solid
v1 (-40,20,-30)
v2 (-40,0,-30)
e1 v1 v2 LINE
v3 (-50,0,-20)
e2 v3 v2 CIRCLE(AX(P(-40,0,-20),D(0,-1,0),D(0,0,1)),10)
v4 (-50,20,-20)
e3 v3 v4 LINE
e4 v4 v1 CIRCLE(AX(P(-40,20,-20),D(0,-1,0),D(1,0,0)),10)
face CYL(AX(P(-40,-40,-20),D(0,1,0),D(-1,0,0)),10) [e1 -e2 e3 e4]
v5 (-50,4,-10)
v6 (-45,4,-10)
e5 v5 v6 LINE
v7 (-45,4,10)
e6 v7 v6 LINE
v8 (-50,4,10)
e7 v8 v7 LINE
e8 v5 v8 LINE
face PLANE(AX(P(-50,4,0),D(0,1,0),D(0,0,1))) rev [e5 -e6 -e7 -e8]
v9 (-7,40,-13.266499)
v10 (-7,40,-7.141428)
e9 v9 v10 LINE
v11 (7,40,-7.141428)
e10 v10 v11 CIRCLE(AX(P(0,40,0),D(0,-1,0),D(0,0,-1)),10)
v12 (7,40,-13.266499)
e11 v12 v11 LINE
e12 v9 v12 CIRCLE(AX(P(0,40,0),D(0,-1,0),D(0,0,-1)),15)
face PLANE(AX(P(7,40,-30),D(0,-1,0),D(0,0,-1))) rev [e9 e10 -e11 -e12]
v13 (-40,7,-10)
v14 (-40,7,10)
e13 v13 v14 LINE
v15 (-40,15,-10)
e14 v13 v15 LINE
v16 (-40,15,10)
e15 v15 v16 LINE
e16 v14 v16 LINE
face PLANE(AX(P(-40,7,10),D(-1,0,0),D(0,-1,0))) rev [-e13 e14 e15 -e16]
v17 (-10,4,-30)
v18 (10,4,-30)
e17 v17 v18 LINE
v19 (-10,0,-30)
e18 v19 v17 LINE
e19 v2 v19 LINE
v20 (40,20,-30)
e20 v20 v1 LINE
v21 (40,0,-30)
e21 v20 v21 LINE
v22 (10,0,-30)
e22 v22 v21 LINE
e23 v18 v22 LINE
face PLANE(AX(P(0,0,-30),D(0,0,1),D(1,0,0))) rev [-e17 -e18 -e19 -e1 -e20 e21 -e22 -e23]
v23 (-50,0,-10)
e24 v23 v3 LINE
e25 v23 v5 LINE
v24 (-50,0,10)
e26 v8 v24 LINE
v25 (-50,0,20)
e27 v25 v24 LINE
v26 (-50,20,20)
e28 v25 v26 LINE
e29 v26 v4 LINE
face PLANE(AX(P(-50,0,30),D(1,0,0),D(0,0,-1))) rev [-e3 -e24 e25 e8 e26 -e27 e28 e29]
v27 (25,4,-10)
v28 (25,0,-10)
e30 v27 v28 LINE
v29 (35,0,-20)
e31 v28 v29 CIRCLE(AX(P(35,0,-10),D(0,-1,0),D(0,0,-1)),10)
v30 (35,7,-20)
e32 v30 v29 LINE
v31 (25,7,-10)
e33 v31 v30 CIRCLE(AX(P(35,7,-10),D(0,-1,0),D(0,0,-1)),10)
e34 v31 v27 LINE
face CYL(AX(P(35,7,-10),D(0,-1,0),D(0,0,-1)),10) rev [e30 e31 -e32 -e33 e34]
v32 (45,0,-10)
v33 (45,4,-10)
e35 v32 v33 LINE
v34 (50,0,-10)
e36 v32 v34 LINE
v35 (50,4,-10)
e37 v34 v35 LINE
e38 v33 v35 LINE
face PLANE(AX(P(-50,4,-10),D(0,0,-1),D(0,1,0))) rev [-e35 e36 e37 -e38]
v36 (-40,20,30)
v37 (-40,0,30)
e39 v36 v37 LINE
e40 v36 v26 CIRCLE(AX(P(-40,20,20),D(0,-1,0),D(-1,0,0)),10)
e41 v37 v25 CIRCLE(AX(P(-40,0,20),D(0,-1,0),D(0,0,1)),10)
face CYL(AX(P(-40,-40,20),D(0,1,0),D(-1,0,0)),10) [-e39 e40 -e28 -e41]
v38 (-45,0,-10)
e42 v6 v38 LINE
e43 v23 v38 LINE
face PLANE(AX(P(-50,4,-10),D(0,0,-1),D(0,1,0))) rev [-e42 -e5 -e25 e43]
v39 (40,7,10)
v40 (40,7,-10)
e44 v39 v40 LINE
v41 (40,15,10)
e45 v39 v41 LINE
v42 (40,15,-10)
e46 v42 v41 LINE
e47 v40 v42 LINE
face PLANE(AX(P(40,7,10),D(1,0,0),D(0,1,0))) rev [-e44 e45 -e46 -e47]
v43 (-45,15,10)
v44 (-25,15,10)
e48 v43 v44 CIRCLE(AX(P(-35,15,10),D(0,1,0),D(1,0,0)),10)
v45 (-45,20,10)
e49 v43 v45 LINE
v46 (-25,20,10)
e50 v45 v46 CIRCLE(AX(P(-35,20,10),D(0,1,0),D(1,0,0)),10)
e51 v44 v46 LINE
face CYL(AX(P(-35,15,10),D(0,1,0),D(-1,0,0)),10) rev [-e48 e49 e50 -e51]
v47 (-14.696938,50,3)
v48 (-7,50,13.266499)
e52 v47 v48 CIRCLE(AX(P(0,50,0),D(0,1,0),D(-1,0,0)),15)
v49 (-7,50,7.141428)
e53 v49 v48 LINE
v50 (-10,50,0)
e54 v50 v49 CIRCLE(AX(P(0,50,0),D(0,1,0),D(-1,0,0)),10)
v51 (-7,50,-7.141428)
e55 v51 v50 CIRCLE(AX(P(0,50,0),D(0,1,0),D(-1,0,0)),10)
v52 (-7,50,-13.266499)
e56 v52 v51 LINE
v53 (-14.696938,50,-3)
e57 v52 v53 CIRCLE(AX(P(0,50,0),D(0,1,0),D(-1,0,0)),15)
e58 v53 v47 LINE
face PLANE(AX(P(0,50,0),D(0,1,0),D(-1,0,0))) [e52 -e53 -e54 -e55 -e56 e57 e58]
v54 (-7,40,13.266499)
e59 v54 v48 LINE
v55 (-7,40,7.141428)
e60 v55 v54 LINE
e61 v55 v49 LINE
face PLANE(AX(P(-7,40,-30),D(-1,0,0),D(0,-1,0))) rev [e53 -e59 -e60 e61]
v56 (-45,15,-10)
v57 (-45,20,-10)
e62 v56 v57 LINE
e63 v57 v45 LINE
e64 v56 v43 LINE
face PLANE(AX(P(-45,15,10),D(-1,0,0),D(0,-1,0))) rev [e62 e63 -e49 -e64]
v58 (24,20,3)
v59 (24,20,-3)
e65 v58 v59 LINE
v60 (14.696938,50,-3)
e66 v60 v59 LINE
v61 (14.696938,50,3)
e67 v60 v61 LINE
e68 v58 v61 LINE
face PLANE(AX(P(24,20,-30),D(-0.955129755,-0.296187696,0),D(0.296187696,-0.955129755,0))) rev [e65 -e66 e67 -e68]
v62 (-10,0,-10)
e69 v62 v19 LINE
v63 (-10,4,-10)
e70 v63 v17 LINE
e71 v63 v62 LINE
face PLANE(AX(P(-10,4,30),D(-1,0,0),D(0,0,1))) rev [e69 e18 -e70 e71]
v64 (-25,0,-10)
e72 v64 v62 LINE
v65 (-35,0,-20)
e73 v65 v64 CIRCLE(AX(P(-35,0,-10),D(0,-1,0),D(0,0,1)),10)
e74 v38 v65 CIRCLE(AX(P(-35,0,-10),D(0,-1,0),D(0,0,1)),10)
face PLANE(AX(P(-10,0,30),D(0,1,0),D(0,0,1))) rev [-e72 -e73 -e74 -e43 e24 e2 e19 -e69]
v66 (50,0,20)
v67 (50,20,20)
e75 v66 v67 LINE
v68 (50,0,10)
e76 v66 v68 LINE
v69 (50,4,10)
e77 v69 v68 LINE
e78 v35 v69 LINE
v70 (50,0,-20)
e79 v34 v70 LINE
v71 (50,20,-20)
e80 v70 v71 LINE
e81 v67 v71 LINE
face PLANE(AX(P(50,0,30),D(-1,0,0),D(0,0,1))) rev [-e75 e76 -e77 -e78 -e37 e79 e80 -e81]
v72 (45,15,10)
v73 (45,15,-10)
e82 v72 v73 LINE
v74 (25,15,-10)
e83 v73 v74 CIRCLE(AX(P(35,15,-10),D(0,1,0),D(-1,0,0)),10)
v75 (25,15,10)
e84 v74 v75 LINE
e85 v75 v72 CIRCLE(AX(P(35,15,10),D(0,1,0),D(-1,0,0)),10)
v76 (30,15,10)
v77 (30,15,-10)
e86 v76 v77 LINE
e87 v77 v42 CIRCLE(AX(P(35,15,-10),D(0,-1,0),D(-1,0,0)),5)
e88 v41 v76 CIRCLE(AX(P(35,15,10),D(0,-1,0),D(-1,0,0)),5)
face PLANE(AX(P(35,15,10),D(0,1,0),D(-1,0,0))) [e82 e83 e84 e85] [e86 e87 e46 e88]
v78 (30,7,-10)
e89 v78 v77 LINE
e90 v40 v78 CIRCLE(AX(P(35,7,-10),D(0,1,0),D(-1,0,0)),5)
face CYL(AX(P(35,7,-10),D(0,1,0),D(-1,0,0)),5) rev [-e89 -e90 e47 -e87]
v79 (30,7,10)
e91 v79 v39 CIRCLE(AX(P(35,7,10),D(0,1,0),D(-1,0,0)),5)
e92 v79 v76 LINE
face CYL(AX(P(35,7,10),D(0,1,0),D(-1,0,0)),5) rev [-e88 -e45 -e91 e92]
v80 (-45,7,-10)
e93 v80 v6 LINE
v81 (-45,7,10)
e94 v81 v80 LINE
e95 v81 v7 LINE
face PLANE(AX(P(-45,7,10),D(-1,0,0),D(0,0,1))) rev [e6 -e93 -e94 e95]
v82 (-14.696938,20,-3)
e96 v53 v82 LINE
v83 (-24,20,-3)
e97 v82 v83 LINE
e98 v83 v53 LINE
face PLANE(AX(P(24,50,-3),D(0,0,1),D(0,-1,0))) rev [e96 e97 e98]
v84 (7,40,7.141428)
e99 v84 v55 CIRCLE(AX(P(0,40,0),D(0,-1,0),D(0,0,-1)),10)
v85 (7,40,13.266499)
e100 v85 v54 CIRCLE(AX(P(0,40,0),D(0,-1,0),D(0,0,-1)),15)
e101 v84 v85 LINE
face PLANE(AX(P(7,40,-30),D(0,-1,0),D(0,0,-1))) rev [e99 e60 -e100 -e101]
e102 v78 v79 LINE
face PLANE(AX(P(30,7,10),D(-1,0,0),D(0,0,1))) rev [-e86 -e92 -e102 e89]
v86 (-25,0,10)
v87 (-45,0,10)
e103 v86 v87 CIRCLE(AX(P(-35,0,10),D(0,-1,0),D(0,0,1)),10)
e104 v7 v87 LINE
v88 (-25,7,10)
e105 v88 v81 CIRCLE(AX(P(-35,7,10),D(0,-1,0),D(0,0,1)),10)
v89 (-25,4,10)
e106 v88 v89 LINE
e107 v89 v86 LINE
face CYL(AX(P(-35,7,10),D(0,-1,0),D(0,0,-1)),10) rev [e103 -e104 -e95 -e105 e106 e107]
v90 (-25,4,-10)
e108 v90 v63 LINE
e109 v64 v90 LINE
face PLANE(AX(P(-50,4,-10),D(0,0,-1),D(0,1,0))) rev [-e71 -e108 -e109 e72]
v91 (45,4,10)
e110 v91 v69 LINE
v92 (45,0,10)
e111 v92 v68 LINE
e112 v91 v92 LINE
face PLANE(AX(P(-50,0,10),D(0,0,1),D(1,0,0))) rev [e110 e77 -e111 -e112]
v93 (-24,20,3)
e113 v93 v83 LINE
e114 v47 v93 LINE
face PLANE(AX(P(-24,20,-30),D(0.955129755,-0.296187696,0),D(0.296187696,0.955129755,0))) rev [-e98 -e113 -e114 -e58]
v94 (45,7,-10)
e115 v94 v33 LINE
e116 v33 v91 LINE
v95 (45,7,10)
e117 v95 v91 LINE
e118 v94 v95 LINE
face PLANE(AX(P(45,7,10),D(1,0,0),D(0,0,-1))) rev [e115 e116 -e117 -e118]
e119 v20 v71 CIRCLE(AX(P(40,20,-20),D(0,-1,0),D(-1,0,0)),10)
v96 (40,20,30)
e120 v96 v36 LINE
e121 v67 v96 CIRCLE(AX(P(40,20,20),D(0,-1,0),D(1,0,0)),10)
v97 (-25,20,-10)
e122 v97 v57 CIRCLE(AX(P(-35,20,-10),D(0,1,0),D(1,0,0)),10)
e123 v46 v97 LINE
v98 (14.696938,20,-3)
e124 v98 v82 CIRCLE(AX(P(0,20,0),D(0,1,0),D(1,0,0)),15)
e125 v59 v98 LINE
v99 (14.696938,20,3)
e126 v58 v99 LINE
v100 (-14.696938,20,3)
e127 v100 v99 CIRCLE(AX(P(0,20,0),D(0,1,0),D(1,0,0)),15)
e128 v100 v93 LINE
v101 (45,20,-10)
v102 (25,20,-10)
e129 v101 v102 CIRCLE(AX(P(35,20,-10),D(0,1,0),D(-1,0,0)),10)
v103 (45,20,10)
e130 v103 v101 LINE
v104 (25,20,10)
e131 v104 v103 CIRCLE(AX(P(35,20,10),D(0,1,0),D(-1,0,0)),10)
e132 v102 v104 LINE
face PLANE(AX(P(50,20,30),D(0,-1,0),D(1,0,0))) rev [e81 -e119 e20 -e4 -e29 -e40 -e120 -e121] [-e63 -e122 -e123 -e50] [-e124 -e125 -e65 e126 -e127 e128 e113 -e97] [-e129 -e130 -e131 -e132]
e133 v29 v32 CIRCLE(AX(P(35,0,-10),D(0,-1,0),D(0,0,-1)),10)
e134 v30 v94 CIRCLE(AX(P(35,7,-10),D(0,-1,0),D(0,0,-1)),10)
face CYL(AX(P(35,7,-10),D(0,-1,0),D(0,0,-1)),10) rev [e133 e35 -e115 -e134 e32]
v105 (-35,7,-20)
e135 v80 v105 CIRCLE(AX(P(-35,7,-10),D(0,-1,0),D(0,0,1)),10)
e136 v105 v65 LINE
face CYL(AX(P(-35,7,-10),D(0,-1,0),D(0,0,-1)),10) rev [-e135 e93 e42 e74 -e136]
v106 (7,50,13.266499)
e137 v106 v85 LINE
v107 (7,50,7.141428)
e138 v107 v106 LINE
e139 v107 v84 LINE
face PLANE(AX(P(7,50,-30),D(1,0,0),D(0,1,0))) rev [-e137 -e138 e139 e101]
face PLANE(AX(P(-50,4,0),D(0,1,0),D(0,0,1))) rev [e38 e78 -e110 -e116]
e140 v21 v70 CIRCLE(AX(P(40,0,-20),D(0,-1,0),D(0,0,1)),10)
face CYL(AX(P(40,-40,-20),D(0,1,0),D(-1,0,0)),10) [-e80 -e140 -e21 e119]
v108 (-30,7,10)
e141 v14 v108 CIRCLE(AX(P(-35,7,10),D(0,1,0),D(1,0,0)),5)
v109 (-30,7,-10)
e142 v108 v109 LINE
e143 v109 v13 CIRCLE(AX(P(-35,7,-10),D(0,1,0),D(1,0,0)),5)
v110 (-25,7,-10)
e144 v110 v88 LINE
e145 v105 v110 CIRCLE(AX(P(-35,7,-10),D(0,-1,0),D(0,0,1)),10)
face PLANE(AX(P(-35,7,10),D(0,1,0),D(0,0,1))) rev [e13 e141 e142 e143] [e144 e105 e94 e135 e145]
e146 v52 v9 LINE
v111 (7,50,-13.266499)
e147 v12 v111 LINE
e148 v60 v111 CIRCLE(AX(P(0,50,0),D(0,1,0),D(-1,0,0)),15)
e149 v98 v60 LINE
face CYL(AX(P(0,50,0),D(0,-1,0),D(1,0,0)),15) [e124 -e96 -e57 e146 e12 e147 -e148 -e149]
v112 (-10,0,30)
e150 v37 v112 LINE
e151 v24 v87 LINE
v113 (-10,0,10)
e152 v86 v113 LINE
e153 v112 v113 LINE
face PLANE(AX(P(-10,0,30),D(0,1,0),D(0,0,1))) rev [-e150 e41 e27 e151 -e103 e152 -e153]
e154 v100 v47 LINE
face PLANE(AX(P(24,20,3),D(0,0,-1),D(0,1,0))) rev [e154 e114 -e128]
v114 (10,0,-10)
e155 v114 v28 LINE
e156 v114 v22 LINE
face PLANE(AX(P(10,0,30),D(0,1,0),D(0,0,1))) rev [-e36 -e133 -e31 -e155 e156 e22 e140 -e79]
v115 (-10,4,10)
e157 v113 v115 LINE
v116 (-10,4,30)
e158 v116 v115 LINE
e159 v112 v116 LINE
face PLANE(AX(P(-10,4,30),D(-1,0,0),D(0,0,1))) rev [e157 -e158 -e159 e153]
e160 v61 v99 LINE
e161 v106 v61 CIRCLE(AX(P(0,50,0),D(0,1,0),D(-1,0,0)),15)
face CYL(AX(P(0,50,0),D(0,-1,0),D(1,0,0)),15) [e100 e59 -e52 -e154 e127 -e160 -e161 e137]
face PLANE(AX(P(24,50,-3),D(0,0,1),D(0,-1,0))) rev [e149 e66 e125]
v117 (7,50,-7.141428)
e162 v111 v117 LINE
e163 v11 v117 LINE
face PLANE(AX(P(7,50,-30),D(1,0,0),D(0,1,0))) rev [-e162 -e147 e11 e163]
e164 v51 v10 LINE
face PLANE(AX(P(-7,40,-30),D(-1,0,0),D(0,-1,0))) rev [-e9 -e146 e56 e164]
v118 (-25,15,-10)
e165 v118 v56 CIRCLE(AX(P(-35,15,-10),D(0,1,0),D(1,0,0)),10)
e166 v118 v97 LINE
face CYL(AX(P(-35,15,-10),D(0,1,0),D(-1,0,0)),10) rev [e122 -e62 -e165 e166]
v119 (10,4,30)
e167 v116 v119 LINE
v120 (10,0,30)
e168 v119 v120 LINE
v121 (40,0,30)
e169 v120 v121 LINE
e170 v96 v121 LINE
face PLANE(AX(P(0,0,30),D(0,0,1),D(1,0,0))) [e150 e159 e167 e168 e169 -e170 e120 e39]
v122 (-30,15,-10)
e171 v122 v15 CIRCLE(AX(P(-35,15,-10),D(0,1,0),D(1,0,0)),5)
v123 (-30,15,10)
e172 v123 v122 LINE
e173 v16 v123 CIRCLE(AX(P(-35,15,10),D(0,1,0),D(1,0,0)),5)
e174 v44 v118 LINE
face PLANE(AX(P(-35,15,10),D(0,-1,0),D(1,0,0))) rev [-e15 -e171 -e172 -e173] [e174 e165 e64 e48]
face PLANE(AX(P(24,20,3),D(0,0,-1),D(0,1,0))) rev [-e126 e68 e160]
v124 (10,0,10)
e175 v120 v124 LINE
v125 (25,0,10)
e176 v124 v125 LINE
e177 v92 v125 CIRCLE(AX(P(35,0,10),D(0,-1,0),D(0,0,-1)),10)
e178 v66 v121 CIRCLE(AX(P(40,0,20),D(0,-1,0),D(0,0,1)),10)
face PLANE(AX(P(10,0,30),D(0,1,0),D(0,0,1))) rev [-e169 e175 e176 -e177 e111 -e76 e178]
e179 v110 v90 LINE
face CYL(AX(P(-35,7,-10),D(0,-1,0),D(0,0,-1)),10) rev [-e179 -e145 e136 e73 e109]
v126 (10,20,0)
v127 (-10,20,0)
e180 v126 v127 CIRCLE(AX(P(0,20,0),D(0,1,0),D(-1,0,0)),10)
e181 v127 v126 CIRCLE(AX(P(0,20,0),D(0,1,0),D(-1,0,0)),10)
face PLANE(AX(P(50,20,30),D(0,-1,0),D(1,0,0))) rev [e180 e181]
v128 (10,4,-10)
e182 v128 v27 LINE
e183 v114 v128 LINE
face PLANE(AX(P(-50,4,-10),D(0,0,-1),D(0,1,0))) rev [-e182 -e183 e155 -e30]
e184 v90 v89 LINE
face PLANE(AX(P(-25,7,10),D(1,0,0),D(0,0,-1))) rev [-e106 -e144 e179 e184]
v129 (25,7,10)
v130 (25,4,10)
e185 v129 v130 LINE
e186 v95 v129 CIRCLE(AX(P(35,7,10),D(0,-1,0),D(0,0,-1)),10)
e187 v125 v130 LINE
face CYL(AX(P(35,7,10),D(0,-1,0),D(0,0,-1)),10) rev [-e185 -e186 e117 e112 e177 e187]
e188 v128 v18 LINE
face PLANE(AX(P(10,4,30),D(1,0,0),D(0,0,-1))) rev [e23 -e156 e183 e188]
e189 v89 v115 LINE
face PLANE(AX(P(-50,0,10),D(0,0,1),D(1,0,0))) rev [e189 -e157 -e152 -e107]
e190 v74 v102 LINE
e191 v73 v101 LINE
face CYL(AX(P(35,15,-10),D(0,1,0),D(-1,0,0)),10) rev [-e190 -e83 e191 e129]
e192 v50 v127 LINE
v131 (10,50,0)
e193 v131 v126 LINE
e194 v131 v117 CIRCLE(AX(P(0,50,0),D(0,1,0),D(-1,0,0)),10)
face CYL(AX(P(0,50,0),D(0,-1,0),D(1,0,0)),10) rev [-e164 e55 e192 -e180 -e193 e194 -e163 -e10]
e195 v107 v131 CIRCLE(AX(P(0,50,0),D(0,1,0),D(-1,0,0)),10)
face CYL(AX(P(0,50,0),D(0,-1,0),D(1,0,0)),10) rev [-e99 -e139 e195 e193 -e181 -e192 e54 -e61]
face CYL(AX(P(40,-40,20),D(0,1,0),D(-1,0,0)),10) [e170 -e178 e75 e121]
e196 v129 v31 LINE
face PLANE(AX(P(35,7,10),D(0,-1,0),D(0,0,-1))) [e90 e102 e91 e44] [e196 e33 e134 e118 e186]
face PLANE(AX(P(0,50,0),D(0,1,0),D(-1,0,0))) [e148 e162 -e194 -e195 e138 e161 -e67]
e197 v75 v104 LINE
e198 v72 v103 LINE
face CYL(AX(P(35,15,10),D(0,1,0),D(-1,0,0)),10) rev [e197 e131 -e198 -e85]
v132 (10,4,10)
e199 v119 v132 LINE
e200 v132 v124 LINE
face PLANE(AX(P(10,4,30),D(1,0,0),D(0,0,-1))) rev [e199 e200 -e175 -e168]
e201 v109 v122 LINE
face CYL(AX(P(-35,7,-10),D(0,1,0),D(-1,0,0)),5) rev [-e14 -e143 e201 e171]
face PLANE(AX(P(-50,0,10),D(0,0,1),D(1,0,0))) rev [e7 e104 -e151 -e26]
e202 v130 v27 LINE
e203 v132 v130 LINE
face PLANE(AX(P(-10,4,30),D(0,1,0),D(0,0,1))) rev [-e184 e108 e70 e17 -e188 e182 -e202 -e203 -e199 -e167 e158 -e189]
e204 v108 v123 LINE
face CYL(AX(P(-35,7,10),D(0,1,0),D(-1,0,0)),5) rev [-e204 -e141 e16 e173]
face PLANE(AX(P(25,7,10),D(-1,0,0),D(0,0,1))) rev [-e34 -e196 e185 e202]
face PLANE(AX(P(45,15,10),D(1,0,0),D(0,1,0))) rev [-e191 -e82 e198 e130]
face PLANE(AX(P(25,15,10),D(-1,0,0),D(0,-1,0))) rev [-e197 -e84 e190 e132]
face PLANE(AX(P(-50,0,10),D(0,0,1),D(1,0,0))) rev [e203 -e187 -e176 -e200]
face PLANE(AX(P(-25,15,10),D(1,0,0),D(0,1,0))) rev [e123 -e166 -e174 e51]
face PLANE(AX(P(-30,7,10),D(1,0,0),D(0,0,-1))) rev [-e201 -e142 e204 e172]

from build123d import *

# Parameters (mm, degrees)
BASE_PLATE_DEPTH         = 30
UNDERSIDE_NOTCHES_DEPTH  = 60
PIVOT_BOSS_SKETCH_R      = 15
PIVOT_BOSS_SKETCH_R_2    = 10
PIVOT_BOSS_30_DEPTH      = 30
SLOT_RECESS_A_DEPTH      = 13
SLOT_INNER_CUT_A_DEPTH   = 5
SLOT_START               = -7
SLOT_RECESS_B_DEPTH      = 7
SLOT_INNER_CUT_B_DEPTH   = 116.758369028
BOSS_SLOT_CUT_DEPTH      = 77.811457479
BOSS_SLOT_CUT_DEPTH_BACK = 77.811457479
SUPPORT_RIB_DEPTH        = 24
RIB_TRIM_CUT_DEPTH       = 77.811457479
RIB_TRIM_CUT_DEPTH_BACK  = 77.811457479
PIVOT_BORE_SKETCH_R      = 10
PIVOT_BORE_20_DEPTH      = 48


with BuildPart() as part:
    # Base Plate Profile Sketch → Base Plate (new, symmetric)
    with BuildSketch(Plane.XY):
        Polygon((-10, 4), (10, 4), (10, 0), (50, 0), (50, 20), (-50, 20), (-50, 0), (-10, 0), align=None)
    extrude(amount=BASE_PLATE_DEPTH, both=True)

    # Underside Notches Sketch → Underside Notches (cut)
    with BuildSketch(Plane(origin=(0, 20, 0), x_dir=(1, 0, 0), z_dir=(0, 1, 0))):
        with BuildLine():
            Line((40, 30), (50, 30))
            Line((50, 30), (50, 20))
            ThreePointArc((50, 20), (47.071067812, 27.071067812), (40, 30))
        make_face()
        with BuildLine():
            Line((-50, 30), (-50, 20))
            ThreePointArc((-50, 20), (-47.071067812, 27.071067812), (-40, 30))
            Line((-40, 30), (-50, 30))
        make_face()
        with BuildLine():
            Line((-50, -30), (-50, -20))
            ThreePointArc((-50, -20), (-47.071067812, -27.071067812), (-40, -30))
            Line((-40, -30), (-50, -30))
        make_face()
        with BuildLine():
            Line((50, -30), (50, -20))
            ThreePointArc((50, -20), (47.071067812, -27.071067812), (40, -30))
            Line((40, -30), (50, -30))
        make_face()
    extrude(amount=-UNDERSIDE_NOTCHES_DEPTH, mode=Mode.SUBTRACT)

    # Pivot Boss Sketch → Pivot Boss Ø30 (add)
    with BuildSketch(Plane(origin=(0, 20, 0), x_dir=(1, 0, 0), z_dir=(0, 1, 0))):
        Circle(PIVOT_BOSS_SKETCH_R)
        with Locations(Location((0, 0, 0), (0, 0, 180))):
            Circle(PIVOT_BOSS_SKETCH_R_2, mode=Mode.SUBTRACT)
    extrude(amount=PIVOT_BOSS_30_DEPTH)

    # Slot Recess A Sketch → Slot Recess A (cut)
    with BuildSketch(Plane(origin=(0, 20, 0), x_dir=(1, 0, 0), z_dir=(0, 1, 0))):
        with BuildLine():
            Line((30, -10), (30, 10))
            ThreePointArc((30, 10), (35, 15), (40, 10))
            Line((40, 10), (40, -10))
            ThreePointArc((40, -10), (35, -15), (30, -10))
        make_face()
        with BuildLine():
            Line((-30, -10), (-30, 10))
            ThreePointArc((-30, 10), (-35, 15), (-40, 10))
            Line((-40, 10), (-40, -10))
            ThreePointArc((-40, -10), (-35, -15), (-30, -10))
        make_face()
    extrude(amount=-SLOT_RECESS_A_DEPTH, mode=Mode.SUBTRACT)

    # Slot Inner Cut A Sketch → Slot Inner Cut A (cut)
    with BuildSketch(Plane(origin=(0, 20, 0), x_dir=(1, 0, 0), z_dir=(0, 1, 0))):
        with BuildLine():
            Line((25, -10), (25, 10))
            ThreePointArc((25, 10), (35, 20), (45, 10))
            Line((45, 10), (45, -10))
            ThreePointArc((45, -10), (35, -20), (25, -10))
        make_face()
        with BuildLine():
            Line((-25, -10), (-25, 10))
            ThreePointArc((-25, 10), (-35, 20), (-45, 10))
            Line((-45, 10), (-45, -10))
            ThreePointArc((-45, -10), (-35, -20), (-25, -10))
        make_face()
    extrude(amount=-SLOT_INNER_CUT_A_DEPTH, mode=Mode.SUBTRACT)

    # Slot Recess B Sketch → Slot Recess B (cut)
    with BuildSketch(Plane.XZ.offset(SLOT_START)):
        with BuildLine():
            Line((45, 10), (45, -10))
            ThreePointArc((45, -10), (35, -20), (25, -10))
            Line((25, -10), (25, 10))
            ThreePointArc((25, 10), (35, 20), (45, 10))
        make_face()
        with BuildLine():
            Line((-45, 10), (-45, -10))
            ThreePointArc((-45, -10), (-35, -20), (-25, -10))
            Line((-25, -10), (-25, 10))
            ThreePointArc((-25, 10), (-35, 20), (-45, 10))
        make_face()
    extrude(amount=SLOT_RECESS_B_DEPTH, mode=Mode.SUBTRACT)

    # Slot Inner Cut B Sketch → Slot Inner Cut B (cut, through all)
    with BuildSketch(Plane(origin=(50, 0, 0), x_dir=(0, 0, -1), z_dir=(1, 0, 0))):
        Polygon((0, 4), (10, 4), (10, 0), (-10, 0), (-10, 4), align=None)
    extrude(amount=-SLOT_INNER_CUT_B_DEPTH, mode=Mode.SUBTRACT)

    # Boss Slot Sketch → Boss Slot Cut (cut, two sides: drawn at the far end of the back side and taken through both)
    with BuildSketch(Plane.XY.offset(-BOSS_SLOT_CUT_DEPTH_BACK)):
        Polygon((0, 50), (7, 50), (7, 40), (-7, 40), (-7, 50), align=None)
    extrude(amount=BOSS_SLOT_CUT_DEPTH + BOSS_SLOT_CUT_DEPTH_BACK, mode=Mode.SUBTRACT)

    # Support Rib Sketch → Support Rib (add, symmetric)
    with BuildSketch(Plane(origin=(0, 0, 0), x_dir=(0, 0, -1), z_dir=(1, 0, 0))):
        Polygon((0, 50), (3, 50), (3, 20), (-3, 20), (-3, 50), align=None)
    extrude(amount=SUPPORT_RIB_DEPTH, both=True)

    # Rib Trim Sketch → Rib Trim Cut (cut, two sides: drawn at the far end of the back side and taken through both)
    with BuildSketch(Plane.XY.offset(-RIB_TRIM_CUT_DEPTH_BACK)):
        Polygon((24, 20), (14.696938457, 50), (24, 50), align=None)
        Polygon((-24, 50), (-24, 20), (-14.696938457, 50), align=None)
    extrude(amount=RIB_TRIM_CUT_DEPTH + RIB_TRIM_CUT_DEPTH_BACK, mode=Mode.SUBTRACT)

    # Pivot Bore Sketch → Pivot Bore Ø20 (cut)
    with BuildSketch(Plane(origin=(0, 20, 0), x_dir=(1, 0, 0), z_dir=(0, 1, 0))):
        with Locations(Location((0, 0, 0), (0, 0, 314.427004001))):
            Circle(PIVOT_BORE_SKETCH_R)
    extrude(amount=PIVOT_BORE_20_DEPTH, mode=Mode.SUBTRACT)


solid = part.part
